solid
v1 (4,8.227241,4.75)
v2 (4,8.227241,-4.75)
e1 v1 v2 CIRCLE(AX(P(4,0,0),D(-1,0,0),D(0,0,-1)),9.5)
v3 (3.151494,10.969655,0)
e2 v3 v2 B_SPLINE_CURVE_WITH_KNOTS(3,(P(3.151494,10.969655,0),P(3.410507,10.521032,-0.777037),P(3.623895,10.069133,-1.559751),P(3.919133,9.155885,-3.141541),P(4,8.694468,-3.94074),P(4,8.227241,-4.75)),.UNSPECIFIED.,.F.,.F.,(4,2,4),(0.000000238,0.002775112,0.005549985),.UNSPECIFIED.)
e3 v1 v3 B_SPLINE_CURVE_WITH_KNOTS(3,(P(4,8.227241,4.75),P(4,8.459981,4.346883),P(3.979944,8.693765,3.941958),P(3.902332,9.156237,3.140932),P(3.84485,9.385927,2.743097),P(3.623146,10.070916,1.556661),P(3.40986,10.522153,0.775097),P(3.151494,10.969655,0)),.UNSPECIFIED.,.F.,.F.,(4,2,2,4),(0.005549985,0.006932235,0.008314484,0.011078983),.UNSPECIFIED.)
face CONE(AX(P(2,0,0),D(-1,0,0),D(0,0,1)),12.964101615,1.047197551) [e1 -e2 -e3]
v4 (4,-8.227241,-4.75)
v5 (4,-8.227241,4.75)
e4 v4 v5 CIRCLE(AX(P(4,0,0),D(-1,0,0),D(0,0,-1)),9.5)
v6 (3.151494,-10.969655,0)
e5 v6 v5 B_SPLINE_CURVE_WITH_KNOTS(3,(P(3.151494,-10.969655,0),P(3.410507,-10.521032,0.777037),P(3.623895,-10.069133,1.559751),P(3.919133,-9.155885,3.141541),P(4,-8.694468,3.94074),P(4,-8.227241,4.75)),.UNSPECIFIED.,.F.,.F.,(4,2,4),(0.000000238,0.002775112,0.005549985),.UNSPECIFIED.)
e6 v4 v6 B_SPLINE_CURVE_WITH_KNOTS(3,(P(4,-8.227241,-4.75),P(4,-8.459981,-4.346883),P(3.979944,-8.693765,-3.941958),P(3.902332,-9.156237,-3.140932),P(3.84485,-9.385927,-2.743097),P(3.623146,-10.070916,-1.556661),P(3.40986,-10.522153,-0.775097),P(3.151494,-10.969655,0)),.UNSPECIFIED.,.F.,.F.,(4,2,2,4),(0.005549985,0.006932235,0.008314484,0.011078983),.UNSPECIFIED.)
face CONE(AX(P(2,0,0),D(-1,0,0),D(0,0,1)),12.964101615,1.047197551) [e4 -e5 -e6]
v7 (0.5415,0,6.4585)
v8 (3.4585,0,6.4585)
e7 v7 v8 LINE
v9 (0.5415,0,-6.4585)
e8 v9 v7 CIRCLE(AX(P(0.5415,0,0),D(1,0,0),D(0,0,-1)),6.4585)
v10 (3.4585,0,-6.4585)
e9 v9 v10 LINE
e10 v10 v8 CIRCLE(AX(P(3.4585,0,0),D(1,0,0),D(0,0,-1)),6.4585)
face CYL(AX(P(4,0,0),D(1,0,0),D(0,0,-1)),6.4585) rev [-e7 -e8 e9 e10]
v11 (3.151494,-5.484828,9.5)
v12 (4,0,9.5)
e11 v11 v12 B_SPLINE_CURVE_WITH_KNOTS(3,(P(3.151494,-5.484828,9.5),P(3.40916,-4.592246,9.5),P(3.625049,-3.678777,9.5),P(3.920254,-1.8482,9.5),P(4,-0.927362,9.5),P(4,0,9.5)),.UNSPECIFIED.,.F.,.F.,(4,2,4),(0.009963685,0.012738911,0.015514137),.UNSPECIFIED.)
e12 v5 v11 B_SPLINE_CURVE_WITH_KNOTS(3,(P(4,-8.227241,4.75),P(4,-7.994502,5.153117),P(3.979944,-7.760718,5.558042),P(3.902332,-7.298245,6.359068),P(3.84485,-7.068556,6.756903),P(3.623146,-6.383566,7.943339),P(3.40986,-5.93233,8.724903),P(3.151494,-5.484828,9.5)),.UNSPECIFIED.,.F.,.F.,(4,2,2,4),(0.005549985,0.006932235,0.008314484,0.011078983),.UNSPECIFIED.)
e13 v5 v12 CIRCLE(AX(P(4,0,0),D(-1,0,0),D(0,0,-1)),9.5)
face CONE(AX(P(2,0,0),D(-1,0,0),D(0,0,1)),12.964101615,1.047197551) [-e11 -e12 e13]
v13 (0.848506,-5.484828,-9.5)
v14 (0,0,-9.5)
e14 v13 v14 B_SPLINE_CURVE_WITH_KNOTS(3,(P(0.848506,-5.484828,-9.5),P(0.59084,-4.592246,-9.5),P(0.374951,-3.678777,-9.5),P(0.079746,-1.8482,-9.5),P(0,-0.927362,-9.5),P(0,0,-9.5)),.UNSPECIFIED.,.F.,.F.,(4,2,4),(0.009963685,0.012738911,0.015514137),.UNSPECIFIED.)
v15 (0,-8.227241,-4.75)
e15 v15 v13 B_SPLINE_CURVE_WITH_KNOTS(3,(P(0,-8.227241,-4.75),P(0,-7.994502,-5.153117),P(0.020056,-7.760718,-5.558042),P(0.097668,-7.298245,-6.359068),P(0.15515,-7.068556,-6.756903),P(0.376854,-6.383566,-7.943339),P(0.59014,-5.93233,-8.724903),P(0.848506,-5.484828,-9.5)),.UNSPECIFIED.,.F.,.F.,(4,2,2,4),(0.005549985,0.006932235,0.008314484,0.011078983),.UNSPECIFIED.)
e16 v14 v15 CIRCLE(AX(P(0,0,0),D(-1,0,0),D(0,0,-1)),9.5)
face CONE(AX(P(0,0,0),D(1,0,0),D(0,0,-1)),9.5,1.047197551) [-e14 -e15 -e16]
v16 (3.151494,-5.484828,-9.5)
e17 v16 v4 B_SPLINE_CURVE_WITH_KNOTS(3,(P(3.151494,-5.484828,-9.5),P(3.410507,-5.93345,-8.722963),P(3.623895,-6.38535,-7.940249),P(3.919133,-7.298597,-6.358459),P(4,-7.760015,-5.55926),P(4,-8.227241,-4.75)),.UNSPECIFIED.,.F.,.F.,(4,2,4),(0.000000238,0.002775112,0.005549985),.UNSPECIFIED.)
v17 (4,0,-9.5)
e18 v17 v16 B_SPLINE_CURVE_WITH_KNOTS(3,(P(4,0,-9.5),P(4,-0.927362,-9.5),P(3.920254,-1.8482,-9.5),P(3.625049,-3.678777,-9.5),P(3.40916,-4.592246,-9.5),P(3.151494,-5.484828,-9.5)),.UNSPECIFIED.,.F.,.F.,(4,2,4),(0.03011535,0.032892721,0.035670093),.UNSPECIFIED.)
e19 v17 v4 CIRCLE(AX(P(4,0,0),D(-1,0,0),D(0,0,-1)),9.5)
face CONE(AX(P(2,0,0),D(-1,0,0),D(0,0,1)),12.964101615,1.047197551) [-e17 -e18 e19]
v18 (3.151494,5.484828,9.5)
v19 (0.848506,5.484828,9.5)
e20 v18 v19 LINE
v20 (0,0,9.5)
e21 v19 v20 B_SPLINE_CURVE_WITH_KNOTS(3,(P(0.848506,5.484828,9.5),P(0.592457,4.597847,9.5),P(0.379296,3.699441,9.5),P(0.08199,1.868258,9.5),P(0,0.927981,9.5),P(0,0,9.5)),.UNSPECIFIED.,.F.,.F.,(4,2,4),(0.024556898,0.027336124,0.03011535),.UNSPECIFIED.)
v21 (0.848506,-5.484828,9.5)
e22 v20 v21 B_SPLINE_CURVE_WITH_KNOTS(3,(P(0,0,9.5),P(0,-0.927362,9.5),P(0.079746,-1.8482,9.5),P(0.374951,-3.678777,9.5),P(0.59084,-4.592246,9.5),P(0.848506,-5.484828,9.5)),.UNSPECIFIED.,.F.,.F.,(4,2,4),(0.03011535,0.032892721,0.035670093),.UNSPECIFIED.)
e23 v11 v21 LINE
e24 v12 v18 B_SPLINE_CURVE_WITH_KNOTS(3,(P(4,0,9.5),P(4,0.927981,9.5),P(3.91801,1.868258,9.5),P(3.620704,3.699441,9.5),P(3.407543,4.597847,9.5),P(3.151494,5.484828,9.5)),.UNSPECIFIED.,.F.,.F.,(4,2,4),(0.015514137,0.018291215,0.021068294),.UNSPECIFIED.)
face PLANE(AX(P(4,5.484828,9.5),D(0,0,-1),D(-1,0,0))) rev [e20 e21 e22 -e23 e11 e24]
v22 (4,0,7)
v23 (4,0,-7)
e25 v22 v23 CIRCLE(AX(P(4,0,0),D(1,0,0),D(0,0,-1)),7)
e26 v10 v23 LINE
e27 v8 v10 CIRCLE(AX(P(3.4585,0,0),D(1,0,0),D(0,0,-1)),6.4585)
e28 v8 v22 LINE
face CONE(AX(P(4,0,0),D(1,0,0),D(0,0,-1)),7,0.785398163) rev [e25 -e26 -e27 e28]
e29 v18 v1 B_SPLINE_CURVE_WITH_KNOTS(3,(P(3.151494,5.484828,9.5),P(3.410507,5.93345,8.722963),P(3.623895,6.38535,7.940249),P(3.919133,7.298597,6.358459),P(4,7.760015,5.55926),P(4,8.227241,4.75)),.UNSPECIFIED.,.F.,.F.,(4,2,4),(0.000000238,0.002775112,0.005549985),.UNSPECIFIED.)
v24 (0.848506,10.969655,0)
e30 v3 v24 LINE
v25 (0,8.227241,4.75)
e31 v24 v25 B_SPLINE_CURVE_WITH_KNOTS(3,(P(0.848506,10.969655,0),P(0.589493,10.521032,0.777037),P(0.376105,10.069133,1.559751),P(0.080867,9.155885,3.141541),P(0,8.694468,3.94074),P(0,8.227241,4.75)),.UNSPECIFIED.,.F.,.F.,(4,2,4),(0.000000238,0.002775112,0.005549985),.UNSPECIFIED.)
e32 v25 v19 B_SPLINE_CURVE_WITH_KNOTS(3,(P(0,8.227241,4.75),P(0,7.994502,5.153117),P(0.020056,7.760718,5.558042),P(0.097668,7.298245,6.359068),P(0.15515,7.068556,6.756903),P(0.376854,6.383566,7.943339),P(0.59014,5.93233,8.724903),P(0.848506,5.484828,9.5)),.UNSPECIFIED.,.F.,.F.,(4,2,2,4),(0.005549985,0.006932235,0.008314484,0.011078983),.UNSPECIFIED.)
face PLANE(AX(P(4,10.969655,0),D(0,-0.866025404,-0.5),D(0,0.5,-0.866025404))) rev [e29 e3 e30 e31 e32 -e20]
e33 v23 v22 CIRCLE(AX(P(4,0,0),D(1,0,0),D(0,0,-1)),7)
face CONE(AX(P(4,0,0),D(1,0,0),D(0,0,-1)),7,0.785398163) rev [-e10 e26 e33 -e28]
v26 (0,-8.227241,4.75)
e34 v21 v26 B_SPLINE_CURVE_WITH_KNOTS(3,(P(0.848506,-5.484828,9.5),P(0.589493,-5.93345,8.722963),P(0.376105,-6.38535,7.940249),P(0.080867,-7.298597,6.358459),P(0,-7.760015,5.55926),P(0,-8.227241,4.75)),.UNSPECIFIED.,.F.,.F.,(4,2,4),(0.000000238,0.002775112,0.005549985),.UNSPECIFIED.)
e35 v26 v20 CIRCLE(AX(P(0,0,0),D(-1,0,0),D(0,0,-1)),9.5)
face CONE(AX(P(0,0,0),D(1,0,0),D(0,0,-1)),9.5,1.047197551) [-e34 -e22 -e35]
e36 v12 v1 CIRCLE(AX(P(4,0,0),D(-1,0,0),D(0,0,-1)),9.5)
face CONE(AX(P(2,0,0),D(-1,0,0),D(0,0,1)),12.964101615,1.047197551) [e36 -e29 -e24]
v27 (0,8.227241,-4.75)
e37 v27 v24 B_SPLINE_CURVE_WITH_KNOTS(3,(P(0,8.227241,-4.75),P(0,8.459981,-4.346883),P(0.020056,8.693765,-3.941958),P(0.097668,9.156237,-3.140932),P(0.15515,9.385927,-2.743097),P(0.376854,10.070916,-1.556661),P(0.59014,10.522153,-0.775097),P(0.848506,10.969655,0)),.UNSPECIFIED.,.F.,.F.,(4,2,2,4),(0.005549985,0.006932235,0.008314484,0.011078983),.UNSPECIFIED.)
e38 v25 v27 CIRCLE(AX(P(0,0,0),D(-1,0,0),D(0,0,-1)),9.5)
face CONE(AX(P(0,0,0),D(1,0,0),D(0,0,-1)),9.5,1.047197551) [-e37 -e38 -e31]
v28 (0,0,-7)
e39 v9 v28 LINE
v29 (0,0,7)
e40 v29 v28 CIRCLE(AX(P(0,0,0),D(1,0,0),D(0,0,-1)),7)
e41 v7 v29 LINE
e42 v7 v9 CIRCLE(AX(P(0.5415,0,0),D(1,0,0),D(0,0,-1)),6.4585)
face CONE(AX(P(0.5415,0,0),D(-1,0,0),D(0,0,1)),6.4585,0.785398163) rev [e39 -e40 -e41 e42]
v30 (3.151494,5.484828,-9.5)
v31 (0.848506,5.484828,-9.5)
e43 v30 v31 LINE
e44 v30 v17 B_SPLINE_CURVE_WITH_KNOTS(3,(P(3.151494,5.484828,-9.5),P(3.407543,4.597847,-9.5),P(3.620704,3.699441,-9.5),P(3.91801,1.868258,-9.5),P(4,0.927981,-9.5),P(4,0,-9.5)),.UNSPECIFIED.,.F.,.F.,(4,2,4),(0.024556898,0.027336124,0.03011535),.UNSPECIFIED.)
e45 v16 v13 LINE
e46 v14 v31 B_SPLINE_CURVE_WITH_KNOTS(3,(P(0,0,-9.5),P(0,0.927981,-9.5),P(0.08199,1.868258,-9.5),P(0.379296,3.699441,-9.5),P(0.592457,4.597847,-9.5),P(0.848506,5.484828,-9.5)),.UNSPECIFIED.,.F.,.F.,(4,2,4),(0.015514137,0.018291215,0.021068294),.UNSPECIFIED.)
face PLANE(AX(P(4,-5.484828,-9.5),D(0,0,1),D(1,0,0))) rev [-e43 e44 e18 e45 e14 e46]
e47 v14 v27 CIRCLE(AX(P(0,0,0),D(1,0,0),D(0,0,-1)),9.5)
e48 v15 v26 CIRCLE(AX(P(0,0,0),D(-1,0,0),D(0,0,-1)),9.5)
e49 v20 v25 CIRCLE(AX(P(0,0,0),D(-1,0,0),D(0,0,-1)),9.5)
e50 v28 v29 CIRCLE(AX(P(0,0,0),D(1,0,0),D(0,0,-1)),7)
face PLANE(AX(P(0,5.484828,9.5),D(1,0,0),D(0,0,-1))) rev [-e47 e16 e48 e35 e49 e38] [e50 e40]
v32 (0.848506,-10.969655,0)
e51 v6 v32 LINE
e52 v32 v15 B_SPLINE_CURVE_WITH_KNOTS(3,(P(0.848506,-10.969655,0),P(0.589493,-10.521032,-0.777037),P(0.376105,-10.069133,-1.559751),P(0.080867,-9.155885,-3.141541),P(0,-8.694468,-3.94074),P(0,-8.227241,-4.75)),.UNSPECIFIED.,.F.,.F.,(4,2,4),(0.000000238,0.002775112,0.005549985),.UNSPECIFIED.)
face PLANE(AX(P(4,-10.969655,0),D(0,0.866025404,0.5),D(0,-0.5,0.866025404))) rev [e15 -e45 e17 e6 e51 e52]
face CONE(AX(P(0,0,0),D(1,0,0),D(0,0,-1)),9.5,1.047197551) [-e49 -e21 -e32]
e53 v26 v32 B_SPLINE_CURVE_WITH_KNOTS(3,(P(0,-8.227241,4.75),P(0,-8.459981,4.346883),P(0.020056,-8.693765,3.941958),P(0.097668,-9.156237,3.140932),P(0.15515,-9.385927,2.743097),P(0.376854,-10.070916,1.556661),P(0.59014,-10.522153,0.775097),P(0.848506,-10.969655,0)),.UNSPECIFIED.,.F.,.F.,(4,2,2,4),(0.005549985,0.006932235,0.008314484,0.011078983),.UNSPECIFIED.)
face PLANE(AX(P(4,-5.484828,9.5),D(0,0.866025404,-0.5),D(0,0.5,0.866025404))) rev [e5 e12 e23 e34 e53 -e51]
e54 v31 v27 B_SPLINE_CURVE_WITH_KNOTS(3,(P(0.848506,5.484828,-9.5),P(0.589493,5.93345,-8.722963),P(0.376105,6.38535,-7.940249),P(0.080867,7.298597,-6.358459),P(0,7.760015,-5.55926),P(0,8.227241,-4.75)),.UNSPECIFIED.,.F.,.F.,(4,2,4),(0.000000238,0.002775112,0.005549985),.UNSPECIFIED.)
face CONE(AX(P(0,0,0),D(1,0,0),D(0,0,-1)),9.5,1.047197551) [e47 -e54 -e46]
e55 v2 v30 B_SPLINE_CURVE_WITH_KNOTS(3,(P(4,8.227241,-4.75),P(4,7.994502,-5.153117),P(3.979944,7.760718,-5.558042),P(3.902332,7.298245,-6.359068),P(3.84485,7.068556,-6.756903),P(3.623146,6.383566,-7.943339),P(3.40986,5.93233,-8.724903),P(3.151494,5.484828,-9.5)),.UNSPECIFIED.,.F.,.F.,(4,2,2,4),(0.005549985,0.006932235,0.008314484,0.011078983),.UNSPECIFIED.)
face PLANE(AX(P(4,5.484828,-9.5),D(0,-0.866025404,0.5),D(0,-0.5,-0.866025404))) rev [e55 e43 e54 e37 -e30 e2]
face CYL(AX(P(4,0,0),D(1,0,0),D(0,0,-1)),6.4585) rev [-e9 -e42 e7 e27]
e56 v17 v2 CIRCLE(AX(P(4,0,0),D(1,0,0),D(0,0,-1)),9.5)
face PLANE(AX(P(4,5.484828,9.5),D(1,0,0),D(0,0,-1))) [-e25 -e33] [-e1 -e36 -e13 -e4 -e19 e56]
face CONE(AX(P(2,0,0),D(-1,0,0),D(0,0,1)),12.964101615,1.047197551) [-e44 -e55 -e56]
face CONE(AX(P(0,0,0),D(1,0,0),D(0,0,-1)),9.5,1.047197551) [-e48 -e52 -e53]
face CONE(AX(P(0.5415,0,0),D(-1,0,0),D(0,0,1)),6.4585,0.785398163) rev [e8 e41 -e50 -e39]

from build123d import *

# Parameters (mm, degrees)
BOSS_EXTRUDE1_DEPTH = 4


with BuildPart() as part:
    # Sketch1 → Boss-Extrude1 (new body)
    with BuildSketch(Plane(origin=(0, 0, 0), x_dir=(0, 0, -1), z_dir=(1, 0, 0))):
        Polygon((-9.5, 5.484827557), (-9.5, -5.484827557), (0, -10.969655115), (9.5, -5.484827557), (9.5, 5.484827557), (0, 10.969655115), align=None)
    extrude(amount=BOSS_EXTRUDE1_DEPTH)

    # Sketch2 → Cut-Revolve1 (revolve, cut)
    with BuildSketch(Plane.XY):
        Polygon((0, 13.95), (0, 9.5), (2, 12.964101615), (4, 9.5), (4, 13.95), align=None)
    revolve(axis=Axis((50, 0, 0), (-1, 0, 0)), mode=Mode.SUBTRACT)

    # Sketch3 → Cut-Revolve2 (revolve, cut)
    with BuildSketch(Plane.XY, mode=Mode.PRIVATE) as cut_revolve2_sk:
        Polygon((0, 0), (0, 7), (0.5415, 6.4585), (3.4585, 6.4585), (4, 7), (4, 0), align=None)
    revolve(cut_revolve2_sk.sketch.rotate(Axis((4, 0, 0), (-1, 0, 0)), 90), axis=Axis((4, 0, 0), (-1, 0, 0)), mode=Mode.SUBTRACT)


solid = part.part
